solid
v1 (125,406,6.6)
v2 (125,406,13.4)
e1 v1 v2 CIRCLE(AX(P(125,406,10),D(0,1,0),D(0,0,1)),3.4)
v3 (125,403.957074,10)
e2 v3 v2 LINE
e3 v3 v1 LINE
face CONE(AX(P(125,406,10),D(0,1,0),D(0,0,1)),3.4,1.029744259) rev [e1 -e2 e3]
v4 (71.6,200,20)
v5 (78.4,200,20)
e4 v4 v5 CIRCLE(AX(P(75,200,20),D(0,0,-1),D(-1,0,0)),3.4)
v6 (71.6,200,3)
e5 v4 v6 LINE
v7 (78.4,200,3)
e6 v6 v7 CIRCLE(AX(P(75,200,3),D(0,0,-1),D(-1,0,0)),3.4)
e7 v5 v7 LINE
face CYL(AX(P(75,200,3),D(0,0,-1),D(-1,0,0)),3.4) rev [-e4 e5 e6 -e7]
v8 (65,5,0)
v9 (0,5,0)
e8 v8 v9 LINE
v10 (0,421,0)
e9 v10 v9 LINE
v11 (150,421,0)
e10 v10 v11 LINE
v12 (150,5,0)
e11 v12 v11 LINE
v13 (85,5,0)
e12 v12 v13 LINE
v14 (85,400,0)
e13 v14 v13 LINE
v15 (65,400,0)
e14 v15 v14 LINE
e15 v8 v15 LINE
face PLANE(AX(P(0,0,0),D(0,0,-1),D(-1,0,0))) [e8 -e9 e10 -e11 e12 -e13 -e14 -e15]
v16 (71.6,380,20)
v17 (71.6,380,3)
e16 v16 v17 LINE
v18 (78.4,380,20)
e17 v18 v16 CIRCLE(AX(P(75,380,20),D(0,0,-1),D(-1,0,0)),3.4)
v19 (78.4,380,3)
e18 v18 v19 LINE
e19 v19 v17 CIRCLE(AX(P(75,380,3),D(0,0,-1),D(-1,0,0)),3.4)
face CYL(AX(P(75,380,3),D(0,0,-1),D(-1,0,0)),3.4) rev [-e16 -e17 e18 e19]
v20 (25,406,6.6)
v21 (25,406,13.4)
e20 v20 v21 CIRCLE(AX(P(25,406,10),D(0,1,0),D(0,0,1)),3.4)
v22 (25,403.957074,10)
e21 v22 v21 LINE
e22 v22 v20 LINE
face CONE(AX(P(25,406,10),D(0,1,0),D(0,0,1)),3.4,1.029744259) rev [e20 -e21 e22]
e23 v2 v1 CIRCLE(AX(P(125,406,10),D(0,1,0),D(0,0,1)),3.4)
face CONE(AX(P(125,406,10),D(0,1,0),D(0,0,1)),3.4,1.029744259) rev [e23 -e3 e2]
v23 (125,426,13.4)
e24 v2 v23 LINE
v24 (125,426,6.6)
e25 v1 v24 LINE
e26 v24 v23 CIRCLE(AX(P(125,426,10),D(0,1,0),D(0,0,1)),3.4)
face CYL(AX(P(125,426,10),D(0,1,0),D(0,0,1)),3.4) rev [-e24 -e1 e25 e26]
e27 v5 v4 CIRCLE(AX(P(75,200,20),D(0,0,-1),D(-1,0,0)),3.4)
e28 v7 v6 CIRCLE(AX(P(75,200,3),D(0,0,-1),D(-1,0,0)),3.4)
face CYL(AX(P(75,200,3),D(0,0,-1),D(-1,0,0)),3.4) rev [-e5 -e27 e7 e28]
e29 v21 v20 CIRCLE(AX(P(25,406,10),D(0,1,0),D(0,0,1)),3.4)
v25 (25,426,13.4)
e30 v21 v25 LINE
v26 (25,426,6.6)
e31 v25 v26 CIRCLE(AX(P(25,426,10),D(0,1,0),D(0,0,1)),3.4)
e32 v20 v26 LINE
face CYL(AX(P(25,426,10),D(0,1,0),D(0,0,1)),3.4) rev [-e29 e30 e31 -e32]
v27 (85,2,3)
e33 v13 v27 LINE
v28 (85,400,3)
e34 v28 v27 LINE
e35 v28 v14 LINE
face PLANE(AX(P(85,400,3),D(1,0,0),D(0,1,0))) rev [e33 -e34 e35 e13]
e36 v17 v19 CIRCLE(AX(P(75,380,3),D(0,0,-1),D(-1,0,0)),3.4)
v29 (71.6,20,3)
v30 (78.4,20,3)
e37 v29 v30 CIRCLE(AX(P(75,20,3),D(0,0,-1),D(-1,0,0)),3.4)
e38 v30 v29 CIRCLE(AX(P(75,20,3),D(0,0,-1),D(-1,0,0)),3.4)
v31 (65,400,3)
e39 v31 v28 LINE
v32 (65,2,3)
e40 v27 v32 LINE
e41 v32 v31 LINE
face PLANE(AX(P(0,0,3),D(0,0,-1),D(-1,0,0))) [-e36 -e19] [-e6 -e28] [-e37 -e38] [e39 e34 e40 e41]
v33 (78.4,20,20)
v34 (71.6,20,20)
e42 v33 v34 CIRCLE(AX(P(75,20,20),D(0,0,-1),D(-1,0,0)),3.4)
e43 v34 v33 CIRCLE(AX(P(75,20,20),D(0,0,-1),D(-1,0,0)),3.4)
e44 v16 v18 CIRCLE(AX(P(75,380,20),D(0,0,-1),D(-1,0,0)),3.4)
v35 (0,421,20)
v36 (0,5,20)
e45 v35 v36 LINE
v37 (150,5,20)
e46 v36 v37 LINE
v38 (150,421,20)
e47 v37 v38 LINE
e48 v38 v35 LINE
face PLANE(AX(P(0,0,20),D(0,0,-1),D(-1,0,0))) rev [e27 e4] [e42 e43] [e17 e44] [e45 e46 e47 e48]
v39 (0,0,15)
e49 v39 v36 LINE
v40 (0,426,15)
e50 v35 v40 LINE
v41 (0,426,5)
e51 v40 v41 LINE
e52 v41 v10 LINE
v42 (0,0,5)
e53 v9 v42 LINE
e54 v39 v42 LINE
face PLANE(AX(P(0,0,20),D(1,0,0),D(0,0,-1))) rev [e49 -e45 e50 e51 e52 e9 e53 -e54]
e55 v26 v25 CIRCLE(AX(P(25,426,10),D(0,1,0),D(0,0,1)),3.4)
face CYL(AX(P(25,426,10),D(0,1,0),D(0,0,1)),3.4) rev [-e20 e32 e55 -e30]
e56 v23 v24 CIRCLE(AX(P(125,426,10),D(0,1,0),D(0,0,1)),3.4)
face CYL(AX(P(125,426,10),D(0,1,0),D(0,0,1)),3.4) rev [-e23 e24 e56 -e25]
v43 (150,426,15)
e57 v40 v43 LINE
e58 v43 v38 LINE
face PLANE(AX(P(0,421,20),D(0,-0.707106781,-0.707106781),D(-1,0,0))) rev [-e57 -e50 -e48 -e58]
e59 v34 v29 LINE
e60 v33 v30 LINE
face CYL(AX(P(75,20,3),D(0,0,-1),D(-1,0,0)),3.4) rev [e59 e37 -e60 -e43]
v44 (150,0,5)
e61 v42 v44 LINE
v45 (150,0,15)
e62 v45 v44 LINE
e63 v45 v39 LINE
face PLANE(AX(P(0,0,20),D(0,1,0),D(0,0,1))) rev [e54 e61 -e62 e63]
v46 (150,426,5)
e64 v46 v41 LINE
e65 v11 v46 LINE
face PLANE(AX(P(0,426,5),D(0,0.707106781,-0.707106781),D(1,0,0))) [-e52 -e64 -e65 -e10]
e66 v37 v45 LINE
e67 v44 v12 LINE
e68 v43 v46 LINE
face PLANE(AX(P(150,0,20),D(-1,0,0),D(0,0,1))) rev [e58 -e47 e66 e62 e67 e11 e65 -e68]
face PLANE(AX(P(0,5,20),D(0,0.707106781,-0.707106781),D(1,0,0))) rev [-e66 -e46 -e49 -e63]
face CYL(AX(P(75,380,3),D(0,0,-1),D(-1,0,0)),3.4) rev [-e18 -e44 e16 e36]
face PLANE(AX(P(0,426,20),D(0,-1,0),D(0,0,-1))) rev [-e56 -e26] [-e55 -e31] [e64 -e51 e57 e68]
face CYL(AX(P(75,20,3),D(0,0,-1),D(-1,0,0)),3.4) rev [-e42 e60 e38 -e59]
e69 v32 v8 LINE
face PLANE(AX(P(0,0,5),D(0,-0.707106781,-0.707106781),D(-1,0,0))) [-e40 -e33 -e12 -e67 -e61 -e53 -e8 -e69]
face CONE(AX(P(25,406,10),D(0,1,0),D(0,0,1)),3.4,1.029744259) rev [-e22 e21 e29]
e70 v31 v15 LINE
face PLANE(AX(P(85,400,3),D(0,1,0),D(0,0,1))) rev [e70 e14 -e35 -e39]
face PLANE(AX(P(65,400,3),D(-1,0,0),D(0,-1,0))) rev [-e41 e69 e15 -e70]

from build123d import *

# Parameters (mm, degrees)
SKETCH1_W             = 150
SKETCH1_H             = 426
BOSS_EXTRUDE1_DEPTH   = 20
SKETCH2_W             = 20
SKETCH2_H             = 400
CUT_EXTRUDE1_DEPTH    = 3
M8_TAPPED_HOLE2_D     = 6.8
M8_TAPPED_HOLE2_DEPTH = 19.75
M8_TAPPED_HOLE2_TIP   = 2.042926105
M8_TAPPED_HOLE1_D     = 6.8
M8_TAPPED_HOLE1_DEPTH = 20
M8_TAPPED_HOLE1_TIP   = 2.042926105
CHAMFER1_SIZE         = 5
CHAMFER2_SIZE         = 5


with BuildPart() as part:
    # Sketch1 → Boss-Extrude1 (new body)
    with BuildSketch(Plane.XY):
        with Locations((75, 213)):
            Rectangle(SKETCH1_W, SKETCH1_H)
    extrude(amount=BOSS_EXTRUDE1_DEPTH)

    # Sketch2 → Cut-Extrude1 (cut)
    with BuildSketch(Plane(origin=(0, 0, 0), x_dir=(-1, 0, 0), z_dir=(0, 0, -1))):
        with Locations((-75, 200)):
            Rectangle(SKETCH2_W, SKETCH2_H)
    extrude(amount=-CUT_EXTRUDE1_DEPTH, mode=Mode.SUBTRACT)

    # M8 Tapped Hole2
    with Locations(Plane(origin=(0, 0, 3), x_dir=(-1, 0, 0), z_dir=(0, 0, -1))):
        with Locations((-75, 20), (-75, 200), (-75, 380)):
            Hole(M8_TAPPED_HOLE2_D / 2, depth=M8_TAPPED_HOLE2_DEPTH)
            with Locations((0, 0, -(M8_TAPPED_HOLE2_DEPTH + M8_TAPPED_HOLE2_TIP / 2))):  # 118° drill point
                Cone(0, M8_TAPPED_HOLE2_D / 2, M8_TAPPED_HOLE2_TIP, mode=Mode.SUBTRACT)

    # M8 Tapped Hole1
    with Locations(Plane(origin=(0, 426, 0), x_dir=(1, 0, 0), z_dir=(0, 1, 0))):
        with Locations((25, -10), (125, -10)):
            Hole(M8_TAPPED_HOLE1_D / 2, depth=M8_TAPPED_HOLE1_DEPTH)
            with Locations((0, 0, -(M8_TAPPED_HOLE1_DEPTH + M8_TAPPED_HOLE1_TIP / 2))):  # 118° drill point
                Cone(0, M8_TAPPED_HOLE1_D / 2, M8_TAPPED_HOLE1_TIP, mode=Mode.SUBTRACT)

    # Chamfer1
    chamfer1_edges = [part.edges().sort_by_distance(p)[0] for p in [
        (75, 0, 20),
        (32.5, 0, 0),
    ]]
    chamfer(chamfer1_edges, length=CHAMFER1_SIZE)

    # Chamfer2
    chamfer2_edges = [part.edges().sort_by_distance(p)[0] for p in [
        (75, 426, 20),
        (75, 426, 0),
    ]]
    chamfer(chamfer2_edges, length=CHAMFER2_SIZE)


solid = part.part
